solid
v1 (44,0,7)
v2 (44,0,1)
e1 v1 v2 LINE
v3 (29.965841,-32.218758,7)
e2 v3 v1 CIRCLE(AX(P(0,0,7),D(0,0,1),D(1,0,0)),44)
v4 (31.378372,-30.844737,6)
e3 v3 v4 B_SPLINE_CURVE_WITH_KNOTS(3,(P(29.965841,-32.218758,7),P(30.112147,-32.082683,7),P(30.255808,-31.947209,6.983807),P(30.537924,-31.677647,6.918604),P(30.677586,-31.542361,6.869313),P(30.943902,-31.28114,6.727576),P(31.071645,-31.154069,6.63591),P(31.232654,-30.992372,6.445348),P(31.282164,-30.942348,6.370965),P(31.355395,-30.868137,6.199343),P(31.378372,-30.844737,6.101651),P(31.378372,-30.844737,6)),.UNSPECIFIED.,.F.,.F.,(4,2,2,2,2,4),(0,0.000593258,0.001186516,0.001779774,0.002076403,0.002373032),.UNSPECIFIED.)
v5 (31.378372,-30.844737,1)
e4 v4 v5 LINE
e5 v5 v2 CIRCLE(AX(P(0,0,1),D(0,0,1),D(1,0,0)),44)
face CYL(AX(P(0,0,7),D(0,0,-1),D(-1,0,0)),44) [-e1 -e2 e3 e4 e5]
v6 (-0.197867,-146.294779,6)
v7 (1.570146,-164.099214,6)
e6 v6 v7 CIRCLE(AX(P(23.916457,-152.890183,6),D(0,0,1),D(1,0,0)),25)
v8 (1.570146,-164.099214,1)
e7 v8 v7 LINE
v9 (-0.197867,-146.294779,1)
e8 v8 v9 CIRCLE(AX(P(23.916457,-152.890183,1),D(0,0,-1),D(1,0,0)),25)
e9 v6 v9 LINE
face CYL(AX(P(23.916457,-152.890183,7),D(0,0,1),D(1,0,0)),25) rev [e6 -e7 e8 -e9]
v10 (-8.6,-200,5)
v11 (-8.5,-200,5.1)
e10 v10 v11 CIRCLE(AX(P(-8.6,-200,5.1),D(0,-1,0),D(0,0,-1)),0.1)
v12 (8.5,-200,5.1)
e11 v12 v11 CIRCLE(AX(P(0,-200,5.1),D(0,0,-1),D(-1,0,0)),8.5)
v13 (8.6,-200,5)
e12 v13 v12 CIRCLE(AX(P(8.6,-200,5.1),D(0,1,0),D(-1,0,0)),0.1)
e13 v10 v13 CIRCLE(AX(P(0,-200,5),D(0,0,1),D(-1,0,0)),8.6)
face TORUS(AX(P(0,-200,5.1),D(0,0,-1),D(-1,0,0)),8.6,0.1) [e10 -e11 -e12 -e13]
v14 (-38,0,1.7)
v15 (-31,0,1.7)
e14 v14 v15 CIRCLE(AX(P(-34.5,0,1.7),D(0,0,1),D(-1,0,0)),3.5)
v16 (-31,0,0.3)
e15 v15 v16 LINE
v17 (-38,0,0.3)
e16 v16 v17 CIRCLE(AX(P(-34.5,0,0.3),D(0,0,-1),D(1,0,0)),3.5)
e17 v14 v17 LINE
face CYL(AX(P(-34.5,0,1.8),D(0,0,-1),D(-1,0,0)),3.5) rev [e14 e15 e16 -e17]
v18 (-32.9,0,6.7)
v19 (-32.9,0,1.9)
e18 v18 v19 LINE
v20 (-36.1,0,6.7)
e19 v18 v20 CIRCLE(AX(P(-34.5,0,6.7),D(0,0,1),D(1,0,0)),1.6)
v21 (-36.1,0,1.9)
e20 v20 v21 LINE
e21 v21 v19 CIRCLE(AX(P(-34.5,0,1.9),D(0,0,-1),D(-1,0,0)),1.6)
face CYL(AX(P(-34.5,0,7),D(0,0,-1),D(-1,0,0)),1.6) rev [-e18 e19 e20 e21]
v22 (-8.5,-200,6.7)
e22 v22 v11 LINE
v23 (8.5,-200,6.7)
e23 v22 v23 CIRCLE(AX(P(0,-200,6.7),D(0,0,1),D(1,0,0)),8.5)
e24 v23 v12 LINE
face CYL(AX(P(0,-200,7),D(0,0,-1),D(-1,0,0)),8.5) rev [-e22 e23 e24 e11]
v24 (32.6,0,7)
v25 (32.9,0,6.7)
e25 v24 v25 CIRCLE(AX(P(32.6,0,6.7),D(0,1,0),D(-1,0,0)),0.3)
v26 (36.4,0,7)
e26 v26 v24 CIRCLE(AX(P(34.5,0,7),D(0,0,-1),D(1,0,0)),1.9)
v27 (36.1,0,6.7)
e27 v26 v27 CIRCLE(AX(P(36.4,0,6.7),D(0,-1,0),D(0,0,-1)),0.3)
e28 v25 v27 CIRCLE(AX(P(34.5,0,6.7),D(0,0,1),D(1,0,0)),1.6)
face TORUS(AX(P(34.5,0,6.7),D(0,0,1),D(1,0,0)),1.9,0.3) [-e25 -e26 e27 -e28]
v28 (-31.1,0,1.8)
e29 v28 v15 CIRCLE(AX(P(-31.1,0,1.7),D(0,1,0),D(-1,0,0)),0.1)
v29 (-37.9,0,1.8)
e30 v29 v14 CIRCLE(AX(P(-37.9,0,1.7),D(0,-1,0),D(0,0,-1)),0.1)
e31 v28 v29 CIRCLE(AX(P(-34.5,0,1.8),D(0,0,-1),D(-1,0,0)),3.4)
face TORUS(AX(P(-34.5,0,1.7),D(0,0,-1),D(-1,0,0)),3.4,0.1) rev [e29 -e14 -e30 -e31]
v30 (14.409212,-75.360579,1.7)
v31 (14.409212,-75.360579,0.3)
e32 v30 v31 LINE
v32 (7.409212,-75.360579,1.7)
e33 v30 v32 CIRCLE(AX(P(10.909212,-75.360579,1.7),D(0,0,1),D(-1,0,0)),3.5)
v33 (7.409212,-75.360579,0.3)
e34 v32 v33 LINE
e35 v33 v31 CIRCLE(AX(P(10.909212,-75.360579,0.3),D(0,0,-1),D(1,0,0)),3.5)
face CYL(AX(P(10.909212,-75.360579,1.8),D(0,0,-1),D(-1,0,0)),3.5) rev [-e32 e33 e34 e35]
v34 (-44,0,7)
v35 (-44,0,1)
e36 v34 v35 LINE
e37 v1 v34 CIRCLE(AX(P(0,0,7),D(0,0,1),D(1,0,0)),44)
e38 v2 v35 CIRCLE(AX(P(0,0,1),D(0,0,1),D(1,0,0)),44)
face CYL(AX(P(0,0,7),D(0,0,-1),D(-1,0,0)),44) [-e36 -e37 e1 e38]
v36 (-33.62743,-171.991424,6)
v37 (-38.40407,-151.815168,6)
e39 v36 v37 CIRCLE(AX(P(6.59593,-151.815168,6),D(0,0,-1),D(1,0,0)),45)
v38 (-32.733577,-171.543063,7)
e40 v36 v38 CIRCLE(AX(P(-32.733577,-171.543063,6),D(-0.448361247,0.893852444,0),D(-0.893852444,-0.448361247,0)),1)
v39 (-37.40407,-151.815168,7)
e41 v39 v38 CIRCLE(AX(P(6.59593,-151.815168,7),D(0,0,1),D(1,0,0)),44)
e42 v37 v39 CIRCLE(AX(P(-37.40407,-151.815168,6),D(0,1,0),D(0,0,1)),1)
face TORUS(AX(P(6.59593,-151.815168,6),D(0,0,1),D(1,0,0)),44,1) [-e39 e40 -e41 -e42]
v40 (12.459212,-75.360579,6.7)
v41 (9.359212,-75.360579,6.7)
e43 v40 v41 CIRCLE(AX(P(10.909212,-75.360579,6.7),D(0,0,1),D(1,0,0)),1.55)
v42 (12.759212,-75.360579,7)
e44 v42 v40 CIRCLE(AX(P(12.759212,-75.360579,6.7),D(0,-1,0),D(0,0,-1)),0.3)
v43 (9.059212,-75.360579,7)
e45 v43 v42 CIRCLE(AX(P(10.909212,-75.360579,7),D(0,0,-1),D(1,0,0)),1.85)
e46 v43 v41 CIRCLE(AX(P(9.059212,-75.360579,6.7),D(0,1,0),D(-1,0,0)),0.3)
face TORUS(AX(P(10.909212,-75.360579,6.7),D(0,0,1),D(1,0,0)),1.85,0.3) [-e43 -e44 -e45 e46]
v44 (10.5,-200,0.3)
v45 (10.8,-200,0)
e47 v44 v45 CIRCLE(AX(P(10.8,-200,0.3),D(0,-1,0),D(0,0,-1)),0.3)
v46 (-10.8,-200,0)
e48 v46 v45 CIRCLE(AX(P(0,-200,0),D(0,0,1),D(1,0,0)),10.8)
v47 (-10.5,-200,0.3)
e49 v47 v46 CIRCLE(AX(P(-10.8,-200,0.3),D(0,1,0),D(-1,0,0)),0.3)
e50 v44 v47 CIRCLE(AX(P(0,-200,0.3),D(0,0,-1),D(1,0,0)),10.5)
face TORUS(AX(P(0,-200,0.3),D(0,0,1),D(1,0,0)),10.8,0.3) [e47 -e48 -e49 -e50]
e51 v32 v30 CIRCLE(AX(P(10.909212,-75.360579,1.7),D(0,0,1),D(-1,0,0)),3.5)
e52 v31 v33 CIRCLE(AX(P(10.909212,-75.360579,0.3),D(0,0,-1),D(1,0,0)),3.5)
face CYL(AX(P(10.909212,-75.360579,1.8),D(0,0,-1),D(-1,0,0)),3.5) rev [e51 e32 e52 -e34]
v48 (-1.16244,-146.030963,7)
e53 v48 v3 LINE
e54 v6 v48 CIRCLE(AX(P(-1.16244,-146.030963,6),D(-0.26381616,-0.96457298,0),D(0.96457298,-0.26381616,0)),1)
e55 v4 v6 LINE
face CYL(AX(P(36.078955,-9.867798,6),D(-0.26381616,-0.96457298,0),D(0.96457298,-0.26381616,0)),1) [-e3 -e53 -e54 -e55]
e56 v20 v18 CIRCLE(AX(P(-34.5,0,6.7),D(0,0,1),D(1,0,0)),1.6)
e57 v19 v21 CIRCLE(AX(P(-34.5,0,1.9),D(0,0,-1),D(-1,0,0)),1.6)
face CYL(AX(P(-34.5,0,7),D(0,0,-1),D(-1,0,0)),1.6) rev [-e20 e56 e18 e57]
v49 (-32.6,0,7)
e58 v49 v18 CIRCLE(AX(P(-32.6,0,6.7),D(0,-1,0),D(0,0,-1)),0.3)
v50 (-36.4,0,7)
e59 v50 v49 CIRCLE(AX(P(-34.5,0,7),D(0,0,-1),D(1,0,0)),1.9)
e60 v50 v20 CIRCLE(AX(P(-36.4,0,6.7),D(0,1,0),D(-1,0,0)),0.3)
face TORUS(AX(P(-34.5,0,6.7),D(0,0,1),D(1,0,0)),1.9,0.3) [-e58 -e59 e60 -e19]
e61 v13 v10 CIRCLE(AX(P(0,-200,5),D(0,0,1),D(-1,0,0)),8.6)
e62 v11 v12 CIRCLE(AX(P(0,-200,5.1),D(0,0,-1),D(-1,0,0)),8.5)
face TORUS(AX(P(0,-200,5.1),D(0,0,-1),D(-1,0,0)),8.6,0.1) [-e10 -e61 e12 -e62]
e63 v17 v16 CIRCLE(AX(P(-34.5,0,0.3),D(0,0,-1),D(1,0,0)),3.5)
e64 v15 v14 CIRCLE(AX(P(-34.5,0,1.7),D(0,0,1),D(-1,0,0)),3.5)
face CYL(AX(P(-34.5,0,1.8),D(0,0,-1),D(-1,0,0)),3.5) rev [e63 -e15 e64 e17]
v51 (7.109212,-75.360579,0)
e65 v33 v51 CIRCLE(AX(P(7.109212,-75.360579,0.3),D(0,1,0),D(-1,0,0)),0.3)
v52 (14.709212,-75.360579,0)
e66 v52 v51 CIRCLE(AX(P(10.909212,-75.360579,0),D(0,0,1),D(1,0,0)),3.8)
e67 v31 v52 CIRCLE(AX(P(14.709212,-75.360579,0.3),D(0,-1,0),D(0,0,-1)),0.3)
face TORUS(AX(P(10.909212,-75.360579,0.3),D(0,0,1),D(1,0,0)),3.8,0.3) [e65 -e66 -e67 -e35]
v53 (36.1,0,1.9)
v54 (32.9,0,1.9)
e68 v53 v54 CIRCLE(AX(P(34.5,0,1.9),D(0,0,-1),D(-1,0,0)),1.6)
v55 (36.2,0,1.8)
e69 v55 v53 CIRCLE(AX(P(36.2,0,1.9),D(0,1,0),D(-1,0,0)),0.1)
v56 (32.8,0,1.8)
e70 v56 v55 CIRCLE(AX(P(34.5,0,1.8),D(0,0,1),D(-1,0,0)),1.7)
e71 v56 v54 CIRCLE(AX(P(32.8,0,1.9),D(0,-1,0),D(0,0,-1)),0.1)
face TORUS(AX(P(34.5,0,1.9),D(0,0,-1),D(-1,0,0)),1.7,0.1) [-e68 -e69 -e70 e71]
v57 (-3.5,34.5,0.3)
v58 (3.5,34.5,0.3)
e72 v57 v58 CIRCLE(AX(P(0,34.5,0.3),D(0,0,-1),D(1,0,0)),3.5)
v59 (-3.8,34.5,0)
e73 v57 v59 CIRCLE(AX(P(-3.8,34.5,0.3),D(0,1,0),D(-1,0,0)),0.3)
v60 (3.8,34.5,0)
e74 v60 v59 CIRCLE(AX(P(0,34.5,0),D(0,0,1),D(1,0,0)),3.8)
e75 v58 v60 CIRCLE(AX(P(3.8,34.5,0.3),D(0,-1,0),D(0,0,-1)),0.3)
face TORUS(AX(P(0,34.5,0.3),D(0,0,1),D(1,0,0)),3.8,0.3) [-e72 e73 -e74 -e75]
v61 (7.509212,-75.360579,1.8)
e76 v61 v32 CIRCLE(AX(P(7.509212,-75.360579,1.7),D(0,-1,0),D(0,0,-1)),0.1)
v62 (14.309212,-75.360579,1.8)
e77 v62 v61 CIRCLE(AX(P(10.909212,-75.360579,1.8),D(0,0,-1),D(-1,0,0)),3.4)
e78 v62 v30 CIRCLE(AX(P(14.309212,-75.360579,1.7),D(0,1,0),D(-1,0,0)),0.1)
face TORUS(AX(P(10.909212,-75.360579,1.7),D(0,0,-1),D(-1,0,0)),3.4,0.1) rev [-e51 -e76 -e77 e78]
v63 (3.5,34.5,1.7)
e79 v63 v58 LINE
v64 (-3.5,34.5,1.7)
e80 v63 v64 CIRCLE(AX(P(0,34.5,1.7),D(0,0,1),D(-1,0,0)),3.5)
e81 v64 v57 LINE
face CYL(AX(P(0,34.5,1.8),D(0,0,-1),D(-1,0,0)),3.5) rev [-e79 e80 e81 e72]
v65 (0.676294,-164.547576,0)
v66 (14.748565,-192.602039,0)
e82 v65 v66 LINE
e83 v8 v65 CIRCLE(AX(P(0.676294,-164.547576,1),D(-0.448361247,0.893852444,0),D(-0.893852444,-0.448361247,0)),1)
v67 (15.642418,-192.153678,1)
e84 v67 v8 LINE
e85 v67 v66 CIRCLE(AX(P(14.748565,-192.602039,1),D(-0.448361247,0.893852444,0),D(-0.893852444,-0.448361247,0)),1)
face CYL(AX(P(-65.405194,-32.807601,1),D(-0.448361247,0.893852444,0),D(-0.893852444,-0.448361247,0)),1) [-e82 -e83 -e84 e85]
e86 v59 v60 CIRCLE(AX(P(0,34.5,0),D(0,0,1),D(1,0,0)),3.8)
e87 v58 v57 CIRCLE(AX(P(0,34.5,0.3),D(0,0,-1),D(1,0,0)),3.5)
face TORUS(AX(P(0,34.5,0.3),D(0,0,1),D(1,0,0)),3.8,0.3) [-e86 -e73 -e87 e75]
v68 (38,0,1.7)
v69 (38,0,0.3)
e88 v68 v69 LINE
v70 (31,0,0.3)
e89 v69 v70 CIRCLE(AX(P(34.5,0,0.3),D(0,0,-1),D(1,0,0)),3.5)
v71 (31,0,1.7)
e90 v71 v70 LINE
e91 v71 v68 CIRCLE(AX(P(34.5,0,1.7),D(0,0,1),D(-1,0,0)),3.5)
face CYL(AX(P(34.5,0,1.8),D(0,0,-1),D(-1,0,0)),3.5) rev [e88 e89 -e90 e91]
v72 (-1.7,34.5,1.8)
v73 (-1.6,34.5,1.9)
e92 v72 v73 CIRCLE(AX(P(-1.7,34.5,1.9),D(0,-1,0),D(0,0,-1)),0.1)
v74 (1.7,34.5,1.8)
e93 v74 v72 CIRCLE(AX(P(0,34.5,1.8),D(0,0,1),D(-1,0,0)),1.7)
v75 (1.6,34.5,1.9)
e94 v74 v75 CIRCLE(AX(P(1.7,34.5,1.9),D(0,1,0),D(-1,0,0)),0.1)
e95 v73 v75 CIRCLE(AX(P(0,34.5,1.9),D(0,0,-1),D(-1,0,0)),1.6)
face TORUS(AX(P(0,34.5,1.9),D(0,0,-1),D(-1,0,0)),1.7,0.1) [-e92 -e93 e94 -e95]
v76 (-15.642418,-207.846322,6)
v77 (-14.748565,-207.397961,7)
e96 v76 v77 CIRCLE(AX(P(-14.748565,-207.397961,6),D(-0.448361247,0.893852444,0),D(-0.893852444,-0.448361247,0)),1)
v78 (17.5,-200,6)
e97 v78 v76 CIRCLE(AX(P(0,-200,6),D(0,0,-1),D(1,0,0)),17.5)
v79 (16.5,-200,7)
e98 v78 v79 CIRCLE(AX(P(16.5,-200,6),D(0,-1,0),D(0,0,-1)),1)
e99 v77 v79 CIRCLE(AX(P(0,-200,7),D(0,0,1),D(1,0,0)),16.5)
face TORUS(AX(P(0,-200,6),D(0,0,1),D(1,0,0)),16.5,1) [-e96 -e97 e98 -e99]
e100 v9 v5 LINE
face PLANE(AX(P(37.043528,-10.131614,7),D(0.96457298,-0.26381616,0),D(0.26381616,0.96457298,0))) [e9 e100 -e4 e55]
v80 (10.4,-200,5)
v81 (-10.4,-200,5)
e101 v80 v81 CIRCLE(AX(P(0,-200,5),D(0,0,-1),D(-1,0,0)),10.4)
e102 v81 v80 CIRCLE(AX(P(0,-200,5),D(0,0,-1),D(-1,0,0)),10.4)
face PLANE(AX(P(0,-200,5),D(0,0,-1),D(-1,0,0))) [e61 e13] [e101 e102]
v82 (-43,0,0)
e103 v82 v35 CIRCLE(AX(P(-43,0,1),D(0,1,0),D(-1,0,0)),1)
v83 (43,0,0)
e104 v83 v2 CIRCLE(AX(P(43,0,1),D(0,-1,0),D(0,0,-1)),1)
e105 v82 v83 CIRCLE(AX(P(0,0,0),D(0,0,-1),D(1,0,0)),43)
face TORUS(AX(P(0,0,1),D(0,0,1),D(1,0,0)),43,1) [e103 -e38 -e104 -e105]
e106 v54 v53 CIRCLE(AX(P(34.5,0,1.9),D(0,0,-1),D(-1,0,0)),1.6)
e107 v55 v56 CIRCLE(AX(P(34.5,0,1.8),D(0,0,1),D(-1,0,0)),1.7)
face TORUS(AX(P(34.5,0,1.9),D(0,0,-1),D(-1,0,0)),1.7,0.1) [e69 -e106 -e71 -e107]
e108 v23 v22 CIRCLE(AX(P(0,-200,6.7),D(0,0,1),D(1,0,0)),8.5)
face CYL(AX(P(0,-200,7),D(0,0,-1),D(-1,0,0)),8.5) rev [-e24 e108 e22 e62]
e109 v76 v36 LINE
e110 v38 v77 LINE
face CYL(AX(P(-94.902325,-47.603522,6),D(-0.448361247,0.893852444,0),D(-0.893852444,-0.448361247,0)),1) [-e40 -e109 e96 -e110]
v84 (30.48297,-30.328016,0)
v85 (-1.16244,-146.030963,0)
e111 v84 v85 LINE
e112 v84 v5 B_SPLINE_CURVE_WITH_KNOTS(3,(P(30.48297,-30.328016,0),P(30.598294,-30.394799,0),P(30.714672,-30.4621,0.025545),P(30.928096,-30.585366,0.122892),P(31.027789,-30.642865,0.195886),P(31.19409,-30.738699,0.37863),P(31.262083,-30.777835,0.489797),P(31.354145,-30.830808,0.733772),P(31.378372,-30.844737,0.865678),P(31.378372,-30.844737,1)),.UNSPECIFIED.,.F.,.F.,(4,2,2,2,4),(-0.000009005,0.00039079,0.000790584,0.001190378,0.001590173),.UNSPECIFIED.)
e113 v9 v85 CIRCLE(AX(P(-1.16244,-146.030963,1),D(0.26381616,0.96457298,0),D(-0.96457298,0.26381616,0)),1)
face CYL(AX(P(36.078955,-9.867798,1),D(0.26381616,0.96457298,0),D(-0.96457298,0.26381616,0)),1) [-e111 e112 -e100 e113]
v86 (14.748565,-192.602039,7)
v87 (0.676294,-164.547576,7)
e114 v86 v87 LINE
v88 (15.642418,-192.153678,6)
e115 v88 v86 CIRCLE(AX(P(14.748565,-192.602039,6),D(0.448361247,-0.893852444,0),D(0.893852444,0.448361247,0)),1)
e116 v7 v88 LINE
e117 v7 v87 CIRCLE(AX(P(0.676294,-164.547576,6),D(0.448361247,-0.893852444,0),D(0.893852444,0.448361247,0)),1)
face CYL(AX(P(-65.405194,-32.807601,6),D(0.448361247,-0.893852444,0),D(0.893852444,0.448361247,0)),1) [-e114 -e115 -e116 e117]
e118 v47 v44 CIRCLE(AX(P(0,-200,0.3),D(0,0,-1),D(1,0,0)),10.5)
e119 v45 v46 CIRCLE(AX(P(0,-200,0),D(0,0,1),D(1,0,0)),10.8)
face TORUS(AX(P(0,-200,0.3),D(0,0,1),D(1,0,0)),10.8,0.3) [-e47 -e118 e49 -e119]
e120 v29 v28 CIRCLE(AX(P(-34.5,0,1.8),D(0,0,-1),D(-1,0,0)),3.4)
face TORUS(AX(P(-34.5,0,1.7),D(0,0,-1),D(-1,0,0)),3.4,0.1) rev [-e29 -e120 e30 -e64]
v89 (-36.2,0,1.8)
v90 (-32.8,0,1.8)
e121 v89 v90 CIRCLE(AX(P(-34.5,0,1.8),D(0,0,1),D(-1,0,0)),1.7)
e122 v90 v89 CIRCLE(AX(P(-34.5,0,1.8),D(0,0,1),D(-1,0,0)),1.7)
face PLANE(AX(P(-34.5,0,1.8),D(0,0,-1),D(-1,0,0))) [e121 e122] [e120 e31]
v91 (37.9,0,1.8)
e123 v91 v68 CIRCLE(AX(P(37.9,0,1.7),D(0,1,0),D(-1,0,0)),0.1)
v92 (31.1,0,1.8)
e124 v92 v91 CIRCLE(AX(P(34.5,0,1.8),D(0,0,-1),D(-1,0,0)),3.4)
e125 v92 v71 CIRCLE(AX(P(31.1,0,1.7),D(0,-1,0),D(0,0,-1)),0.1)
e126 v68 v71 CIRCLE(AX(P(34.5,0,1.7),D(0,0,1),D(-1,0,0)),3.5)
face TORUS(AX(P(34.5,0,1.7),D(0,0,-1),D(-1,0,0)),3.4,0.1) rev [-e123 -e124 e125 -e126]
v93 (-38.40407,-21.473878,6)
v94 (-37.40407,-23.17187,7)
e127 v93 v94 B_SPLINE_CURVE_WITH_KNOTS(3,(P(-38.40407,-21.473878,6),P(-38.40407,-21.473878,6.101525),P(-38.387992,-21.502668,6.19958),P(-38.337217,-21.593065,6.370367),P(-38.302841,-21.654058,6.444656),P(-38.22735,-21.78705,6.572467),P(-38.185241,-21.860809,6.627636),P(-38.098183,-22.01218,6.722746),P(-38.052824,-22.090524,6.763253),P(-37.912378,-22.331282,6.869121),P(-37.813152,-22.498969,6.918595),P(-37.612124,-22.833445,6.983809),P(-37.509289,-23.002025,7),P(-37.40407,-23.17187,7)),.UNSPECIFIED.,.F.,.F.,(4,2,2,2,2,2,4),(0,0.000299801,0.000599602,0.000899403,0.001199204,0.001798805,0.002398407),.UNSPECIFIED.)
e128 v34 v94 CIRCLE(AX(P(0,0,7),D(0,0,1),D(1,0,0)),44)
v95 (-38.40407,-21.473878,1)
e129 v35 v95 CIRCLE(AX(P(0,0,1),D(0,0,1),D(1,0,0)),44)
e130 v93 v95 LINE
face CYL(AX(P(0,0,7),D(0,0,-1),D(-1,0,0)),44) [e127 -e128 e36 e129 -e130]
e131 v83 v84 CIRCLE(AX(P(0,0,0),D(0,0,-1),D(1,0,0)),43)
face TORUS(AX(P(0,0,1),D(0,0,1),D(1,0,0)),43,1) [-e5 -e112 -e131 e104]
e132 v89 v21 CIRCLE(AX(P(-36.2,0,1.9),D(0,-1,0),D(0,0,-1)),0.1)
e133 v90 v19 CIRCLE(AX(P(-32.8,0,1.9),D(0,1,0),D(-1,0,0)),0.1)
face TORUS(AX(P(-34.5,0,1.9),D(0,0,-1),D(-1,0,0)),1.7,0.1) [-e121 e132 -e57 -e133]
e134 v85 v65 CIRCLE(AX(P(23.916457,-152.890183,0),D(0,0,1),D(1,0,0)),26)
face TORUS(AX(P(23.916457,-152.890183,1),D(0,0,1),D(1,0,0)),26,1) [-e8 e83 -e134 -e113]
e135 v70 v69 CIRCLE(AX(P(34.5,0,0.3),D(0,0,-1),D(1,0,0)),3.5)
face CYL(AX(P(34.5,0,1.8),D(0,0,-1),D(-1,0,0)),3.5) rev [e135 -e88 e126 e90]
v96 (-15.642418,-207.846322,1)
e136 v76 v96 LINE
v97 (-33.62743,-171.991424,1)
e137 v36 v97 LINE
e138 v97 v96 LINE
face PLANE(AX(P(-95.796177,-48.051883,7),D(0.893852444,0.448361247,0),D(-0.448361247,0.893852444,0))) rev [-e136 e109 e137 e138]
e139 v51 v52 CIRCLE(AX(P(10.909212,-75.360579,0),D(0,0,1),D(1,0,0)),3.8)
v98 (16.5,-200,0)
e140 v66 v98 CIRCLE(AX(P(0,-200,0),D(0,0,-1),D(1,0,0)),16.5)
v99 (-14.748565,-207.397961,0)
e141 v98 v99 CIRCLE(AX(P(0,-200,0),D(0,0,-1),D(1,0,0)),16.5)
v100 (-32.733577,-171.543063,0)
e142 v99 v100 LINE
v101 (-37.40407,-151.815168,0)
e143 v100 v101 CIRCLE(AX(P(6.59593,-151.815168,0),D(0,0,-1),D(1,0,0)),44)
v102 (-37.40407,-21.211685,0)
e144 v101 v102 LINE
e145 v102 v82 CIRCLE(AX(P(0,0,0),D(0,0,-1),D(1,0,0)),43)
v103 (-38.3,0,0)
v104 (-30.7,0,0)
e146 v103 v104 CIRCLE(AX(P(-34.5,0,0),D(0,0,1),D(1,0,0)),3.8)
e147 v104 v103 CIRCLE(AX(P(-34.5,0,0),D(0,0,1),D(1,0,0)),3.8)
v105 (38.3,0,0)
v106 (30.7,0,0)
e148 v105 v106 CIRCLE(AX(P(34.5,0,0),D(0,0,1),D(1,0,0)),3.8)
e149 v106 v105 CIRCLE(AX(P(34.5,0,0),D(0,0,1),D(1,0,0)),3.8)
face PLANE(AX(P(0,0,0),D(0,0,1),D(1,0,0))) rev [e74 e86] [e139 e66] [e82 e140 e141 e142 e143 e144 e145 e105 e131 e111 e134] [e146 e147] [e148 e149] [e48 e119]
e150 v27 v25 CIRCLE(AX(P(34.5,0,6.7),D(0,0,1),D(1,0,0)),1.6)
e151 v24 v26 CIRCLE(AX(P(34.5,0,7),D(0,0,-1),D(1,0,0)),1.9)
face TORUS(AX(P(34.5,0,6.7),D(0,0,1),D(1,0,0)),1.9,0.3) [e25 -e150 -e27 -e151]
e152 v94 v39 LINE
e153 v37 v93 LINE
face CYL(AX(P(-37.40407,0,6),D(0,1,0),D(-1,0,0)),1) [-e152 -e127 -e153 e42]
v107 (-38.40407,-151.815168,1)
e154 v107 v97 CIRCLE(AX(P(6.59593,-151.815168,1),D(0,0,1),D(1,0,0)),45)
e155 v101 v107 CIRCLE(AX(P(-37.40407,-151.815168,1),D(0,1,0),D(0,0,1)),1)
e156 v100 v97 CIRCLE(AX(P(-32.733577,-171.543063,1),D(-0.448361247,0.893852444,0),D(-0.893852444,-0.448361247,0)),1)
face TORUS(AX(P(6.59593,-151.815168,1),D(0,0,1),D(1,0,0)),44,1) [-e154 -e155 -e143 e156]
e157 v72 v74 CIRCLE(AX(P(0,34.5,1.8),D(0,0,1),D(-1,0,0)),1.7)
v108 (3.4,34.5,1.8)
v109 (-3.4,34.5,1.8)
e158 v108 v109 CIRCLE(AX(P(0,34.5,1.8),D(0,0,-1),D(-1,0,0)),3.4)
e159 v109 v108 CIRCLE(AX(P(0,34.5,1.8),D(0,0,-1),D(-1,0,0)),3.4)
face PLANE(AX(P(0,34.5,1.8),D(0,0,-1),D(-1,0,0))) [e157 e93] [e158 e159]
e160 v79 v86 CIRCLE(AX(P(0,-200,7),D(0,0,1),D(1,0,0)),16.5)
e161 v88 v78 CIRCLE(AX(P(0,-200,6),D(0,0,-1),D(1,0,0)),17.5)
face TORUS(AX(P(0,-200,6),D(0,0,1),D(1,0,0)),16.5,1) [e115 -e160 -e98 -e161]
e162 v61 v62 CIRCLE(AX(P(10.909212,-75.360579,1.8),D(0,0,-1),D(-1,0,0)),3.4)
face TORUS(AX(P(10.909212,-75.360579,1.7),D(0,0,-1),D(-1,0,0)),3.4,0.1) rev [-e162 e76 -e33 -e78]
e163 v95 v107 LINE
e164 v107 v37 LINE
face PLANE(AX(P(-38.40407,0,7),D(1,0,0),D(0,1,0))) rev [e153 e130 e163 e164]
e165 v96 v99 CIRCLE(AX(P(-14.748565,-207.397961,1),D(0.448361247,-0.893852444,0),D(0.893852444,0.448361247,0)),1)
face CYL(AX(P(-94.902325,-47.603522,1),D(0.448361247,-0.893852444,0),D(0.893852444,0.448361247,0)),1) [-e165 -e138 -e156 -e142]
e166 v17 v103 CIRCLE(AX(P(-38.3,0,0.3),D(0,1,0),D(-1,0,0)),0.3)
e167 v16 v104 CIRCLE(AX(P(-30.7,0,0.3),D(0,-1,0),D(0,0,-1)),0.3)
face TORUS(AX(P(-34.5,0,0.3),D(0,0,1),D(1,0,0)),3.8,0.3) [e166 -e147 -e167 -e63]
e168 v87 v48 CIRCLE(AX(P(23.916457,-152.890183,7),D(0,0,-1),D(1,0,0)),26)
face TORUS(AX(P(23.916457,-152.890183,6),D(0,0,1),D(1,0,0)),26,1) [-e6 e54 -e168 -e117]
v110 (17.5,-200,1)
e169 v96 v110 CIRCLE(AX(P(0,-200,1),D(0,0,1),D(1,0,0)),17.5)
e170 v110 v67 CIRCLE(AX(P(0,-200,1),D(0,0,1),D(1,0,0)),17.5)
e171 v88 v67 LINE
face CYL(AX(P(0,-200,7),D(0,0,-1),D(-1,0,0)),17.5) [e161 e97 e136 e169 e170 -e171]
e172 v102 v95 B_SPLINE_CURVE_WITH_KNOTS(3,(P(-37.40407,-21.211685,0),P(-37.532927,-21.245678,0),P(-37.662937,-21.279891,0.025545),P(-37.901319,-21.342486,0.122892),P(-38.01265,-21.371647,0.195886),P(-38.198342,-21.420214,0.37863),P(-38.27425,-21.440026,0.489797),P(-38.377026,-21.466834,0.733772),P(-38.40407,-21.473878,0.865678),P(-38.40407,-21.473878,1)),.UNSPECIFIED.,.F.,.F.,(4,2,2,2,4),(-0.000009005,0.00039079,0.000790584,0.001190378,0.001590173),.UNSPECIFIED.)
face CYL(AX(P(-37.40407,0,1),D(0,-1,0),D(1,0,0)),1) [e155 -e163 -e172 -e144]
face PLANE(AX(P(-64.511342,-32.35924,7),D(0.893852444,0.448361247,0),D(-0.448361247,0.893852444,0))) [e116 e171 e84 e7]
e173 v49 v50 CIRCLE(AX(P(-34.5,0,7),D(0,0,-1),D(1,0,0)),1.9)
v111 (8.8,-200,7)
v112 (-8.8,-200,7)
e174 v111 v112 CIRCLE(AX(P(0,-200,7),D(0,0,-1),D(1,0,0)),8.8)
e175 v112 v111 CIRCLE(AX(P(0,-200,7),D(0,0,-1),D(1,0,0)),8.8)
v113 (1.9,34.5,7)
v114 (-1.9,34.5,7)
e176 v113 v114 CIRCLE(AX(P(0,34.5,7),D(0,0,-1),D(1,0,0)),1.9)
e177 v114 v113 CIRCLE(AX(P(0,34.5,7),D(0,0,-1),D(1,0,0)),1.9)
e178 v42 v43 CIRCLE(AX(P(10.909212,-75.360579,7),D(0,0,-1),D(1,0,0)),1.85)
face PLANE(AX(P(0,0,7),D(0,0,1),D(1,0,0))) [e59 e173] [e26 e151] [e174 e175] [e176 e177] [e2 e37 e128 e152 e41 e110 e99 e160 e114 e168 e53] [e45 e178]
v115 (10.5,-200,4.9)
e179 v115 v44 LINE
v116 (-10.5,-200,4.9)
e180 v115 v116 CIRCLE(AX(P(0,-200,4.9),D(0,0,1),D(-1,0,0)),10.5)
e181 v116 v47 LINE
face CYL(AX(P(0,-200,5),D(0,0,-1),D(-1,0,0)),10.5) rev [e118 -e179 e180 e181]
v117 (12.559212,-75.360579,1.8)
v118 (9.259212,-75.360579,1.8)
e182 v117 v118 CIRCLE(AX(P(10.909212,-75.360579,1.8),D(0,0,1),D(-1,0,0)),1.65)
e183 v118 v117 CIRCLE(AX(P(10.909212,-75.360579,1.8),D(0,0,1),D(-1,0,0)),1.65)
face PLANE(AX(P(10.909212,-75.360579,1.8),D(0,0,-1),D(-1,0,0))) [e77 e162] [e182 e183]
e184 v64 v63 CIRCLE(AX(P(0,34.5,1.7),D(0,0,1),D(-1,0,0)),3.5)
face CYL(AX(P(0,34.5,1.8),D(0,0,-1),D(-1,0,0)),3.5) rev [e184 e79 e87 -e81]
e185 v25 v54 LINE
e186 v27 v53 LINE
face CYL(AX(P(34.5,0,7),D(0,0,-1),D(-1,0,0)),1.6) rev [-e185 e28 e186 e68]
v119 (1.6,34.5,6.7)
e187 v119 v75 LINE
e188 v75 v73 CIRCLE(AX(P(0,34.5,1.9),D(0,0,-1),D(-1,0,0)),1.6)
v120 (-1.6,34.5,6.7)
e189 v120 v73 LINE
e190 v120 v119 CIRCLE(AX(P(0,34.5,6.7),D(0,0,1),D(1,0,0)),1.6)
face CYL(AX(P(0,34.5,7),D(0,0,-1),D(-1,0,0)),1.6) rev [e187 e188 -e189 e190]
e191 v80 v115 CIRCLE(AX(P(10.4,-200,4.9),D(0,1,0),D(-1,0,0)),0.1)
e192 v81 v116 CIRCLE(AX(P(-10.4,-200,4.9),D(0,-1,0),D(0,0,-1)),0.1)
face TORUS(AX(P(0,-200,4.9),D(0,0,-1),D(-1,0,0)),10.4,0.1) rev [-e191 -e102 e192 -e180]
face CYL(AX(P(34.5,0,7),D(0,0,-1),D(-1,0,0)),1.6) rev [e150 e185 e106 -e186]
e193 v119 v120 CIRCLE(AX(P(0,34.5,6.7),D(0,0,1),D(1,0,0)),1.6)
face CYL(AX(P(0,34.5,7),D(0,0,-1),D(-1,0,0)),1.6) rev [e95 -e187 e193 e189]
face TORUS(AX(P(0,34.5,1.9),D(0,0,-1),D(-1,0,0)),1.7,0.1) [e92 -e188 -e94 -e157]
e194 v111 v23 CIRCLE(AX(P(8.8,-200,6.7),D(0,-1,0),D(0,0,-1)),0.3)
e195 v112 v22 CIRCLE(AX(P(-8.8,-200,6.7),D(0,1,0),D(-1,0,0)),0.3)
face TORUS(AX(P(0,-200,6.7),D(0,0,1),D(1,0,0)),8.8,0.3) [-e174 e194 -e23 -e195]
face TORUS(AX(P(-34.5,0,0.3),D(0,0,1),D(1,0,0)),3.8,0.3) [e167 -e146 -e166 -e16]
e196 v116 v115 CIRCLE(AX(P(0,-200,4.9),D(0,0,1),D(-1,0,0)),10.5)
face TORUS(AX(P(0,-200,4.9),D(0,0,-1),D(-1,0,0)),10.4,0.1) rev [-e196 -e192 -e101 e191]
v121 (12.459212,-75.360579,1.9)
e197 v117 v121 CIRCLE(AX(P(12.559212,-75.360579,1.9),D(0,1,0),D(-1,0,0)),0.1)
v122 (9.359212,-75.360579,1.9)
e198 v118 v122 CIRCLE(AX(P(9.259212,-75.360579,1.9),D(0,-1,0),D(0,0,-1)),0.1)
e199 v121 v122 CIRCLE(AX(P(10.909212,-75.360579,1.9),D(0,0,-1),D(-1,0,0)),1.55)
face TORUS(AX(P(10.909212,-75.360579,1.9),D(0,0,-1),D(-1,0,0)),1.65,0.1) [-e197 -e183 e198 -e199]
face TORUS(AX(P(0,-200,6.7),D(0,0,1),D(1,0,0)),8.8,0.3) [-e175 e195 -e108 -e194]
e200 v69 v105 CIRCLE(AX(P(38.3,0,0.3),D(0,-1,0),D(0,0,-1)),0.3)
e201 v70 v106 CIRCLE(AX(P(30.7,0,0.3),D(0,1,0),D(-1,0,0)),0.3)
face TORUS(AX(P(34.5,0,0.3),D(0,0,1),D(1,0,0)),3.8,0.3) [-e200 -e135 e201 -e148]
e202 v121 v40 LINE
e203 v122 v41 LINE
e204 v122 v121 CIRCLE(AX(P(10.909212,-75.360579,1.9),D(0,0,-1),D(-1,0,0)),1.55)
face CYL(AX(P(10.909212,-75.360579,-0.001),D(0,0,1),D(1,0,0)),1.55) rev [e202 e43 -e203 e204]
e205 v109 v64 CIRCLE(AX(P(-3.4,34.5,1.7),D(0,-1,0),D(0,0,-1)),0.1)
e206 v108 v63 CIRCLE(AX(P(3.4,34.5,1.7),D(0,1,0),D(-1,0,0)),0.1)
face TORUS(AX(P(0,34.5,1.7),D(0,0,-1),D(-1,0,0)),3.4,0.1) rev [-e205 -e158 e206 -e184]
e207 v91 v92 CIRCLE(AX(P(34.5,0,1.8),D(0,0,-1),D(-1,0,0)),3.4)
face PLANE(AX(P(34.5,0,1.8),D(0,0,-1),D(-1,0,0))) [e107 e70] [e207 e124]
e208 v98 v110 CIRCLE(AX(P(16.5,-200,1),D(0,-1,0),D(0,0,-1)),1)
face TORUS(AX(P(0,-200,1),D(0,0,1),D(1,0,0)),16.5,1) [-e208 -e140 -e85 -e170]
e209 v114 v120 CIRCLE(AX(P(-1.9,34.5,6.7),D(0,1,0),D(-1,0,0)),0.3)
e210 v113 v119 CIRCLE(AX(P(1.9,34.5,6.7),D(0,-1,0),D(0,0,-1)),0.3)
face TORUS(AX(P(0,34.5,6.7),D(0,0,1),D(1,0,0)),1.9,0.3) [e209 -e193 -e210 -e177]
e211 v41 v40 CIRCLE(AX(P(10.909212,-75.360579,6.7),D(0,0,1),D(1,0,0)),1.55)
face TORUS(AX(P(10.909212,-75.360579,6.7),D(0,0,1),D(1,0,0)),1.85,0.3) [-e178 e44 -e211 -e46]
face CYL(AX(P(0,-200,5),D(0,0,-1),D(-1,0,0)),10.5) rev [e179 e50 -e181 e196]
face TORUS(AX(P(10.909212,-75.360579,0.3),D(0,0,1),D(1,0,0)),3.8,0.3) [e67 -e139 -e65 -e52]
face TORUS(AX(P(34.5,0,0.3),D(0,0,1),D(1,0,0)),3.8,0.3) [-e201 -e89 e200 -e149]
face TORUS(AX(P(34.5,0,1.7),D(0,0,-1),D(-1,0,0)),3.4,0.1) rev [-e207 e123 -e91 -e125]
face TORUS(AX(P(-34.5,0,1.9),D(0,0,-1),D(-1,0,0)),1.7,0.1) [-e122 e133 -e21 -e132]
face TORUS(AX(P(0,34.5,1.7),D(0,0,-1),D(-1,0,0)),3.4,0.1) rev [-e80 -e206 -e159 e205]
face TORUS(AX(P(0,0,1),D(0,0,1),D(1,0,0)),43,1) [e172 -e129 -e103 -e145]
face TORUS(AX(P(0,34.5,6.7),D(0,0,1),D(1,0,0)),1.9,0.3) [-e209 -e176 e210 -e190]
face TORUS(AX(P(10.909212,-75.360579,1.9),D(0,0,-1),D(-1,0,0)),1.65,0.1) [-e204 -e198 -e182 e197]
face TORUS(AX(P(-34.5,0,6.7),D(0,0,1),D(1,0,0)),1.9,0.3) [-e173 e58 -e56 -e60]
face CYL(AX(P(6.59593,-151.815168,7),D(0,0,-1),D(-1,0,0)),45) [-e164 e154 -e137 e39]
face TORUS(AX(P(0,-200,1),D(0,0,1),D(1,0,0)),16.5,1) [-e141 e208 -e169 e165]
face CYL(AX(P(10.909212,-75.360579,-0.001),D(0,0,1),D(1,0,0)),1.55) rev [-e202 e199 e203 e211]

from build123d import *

# Parameters (mm, degrees)
SKETCH1_R           = 8.5
SKETCH1_R_2         = 1.6
BOSS_EXTRUDE1_DEPTH = 7
FILLET1_R           = 25
FILLET2_R           = 45
SKETCH2_R           = 10.5
CUT_EXTRUDE1_DEPTH  = 5
CUT_EXTRUDE2_REACH  = 224.016
SKETCH3_R           = 1.55
SKETCH5_R           = 3.5
CUT_EXTRUDE4_DEPTH  = 1.8
FILLET3_R           = 1
FILLET5_R           = 0.3
FILLET6_R           = 0.1


with BuildPart() as part:
    # Sketch1 → Boss-Extrude1 (new body)
    with BuildSketch(Plane.XY):
        with BuildLine():
            Line((-38.404069543, -21.473878143), (-38.404069543, -162.468720195))
            Line((-38.404069543, -162.468720195), (-15.642417773, -207.846321828))
            ThreePointArc((-15.642417773, -207.846321828), (7.846321828, -215.642417773), (15.642417773, -192.153678172))
            Line((15.642417773, -192.153678172), (-2.725328205, -155.535761851))
            Line((-2.725328205, -155.535761851), (31.378371719, -30.8447368))
            ThreePointArc((31.378371719, -30.8447368), (5.856052892, 43.608561597), (-38.404069543, -21.473878143))
        make_face()
        with Locations((0, -200)):
            Circle(SKETCH1_R, mode=Mode.SUBTRACT)
        with Locations((-34.5, 0)):
            Circle(SKETCH1_R_2, mode=Mode.SUBTRACT)
        with Locations((0, 34.5)):
            Circle(SKETCH1_R_2, mode=Mode.SUBTRACT)
        with Locations((34.5, 0)):
            Circle(SKETCH1_R_2, mode=Mode.SUBTRACT)
    extrude(amount=BOSS_EXTRUDE1_DEPTH)

    # Fillet1
    fillet1_edges = [part.edges().sort_by_distance(p)[0] for p in [
        (-2.725328205, -155.535761851, 3.5),
    ]]
    fillet(fillet1_edges, radius=FILLET1_R)

    # Fillet2
    fillet2_edges = [part.edges().sort_by_distance(p)[0] for p in [
        (-38.404069543, -162.468720195, 3.5),
    ]]
    fillet(fillet2_edges, radius=FILLET2_R)

    # Sketch2 → Cut-Extrude1 (cut)
    with BuildSketch(Plane(origin=(0, 0, 0), x_dir=(-1, 0, 0), z_dir=(0, 0, -1))):
        with Locations((0, -200)):
            Circle(SKETCH2_R)
    extrude(amount=-CUT_EXTRUDE1_DEPTH, mode=Mode.SUBTRACT)

    # Sketch3 → Cut-Extrude2 (cut, up to next)
    with BuildSketch(Plane.XY.offset(7), mode=Mode.PRIVATE) as cut_extrude2_sk1:
        with Locations((10.909211738, -75.36057928)):
            Circle(SKETCH3_R)
    cut_extrude2_tool1 = extrude(cut_extrude2_sk1.sketch, amount=-CUT_EXTRUDE2_REACH, mode=Mode.PRIVATE) & part.part
    add(cut_extrude2_tool1.solids().sort_by_distance((10.909212, -75.360579, 7))[0], mode=Mode.SUBTRACT)

    # Sketch5 → Cut-Extrude4 (cut)
    with BuildSketch(Plane(origin=(0, 0, 0), x_dir=(-1, 0, 0), z_dir=(0, 0, -1))):
        with Locations((0, 34.5)):
            Circle(SKETCH5_R)
        with Locations((-10.909211738, -75.36057928)):
            Circle(SKETCH5_R)
        with Locations((34.5, 0)):
            Circle(SKETCH5_R)
        with Locations((-34.5, 0)):
            Circle(SKETCH5_R)
    extrude(amount=-CUT_EXTRUDE4_DEPTH, mode=Mode.SUBTRACT)

    # Fillet3
    fillet3_edges = [part.edges().sort_by_distance(p)[0] for p in [
        (7.846321828, -215.642417773, 0),
        (-38.404069543, -86.644523001, 0),
        (5.856052892, 43.608561597, 0),
        (15.590252243, -88.569757998, 0),
        (15.590252243, -88.569757998, 7),
        (8.606281967, -178.12644628, 0),
        (8.606281967, -178.12644628, 7),
        (-0.961186177, -155.36057928, 0),
        (-0.961186177, -155.36057928, 7),
        (-38.404069543, -86.644523001, 7),
        (-24.634923651, -189.918872908, 0),
        (-24.634923651, -189.918872908, 7),
        (-37.19362994, -162.182153935, 0),
        (-37.19362994, -162.182153935, 7),
        (7.846321828, -215.642417773, 7),
    ]]
    fillet(fillet3_edges, radius=FILLET3_R)

    # Fillet5
    fillet5_edges = [part.edges().sort_by_distance(p)[0] for p in [
        (32.9, 0, 7),
        (-36.1, 0, 7),
        (-8.5, -200, 7),
        (-1.6, 34.5, 7),
        (10.5, -200, 0),
        (9.359211738, -75.36057928, 7),
        (3.5, 34.5, 0),
        (14.409211738, -75.36057928, 0),
        (-31, 0, 0),
        (38, 0, 0),
    ]]
    fillet(fillet5_edges, radius=FILLET5_R)

    # Fillet6
    fillet6_edges = [part.edges().sort_by_distance(p)[0] for p in [
        (10.5, -200, 5),
        (-8.5, -200, 5),
        (3.5, 34.5, 1.8),
        (-1.6, 34.5, 1.8),
        (14.409211738, -75.36057928, 1.8),
        (9.359211738, -75.36057928, 1.8),
        (-31, 0, 1.8),
        (-36.1, 0, 1.8),
        (38, 0, 1.8),
        (32.9, 0, 1.8),
    ]]
    fillet(fillet6_edges, radius=FILLET6_R)


solid = part.part
